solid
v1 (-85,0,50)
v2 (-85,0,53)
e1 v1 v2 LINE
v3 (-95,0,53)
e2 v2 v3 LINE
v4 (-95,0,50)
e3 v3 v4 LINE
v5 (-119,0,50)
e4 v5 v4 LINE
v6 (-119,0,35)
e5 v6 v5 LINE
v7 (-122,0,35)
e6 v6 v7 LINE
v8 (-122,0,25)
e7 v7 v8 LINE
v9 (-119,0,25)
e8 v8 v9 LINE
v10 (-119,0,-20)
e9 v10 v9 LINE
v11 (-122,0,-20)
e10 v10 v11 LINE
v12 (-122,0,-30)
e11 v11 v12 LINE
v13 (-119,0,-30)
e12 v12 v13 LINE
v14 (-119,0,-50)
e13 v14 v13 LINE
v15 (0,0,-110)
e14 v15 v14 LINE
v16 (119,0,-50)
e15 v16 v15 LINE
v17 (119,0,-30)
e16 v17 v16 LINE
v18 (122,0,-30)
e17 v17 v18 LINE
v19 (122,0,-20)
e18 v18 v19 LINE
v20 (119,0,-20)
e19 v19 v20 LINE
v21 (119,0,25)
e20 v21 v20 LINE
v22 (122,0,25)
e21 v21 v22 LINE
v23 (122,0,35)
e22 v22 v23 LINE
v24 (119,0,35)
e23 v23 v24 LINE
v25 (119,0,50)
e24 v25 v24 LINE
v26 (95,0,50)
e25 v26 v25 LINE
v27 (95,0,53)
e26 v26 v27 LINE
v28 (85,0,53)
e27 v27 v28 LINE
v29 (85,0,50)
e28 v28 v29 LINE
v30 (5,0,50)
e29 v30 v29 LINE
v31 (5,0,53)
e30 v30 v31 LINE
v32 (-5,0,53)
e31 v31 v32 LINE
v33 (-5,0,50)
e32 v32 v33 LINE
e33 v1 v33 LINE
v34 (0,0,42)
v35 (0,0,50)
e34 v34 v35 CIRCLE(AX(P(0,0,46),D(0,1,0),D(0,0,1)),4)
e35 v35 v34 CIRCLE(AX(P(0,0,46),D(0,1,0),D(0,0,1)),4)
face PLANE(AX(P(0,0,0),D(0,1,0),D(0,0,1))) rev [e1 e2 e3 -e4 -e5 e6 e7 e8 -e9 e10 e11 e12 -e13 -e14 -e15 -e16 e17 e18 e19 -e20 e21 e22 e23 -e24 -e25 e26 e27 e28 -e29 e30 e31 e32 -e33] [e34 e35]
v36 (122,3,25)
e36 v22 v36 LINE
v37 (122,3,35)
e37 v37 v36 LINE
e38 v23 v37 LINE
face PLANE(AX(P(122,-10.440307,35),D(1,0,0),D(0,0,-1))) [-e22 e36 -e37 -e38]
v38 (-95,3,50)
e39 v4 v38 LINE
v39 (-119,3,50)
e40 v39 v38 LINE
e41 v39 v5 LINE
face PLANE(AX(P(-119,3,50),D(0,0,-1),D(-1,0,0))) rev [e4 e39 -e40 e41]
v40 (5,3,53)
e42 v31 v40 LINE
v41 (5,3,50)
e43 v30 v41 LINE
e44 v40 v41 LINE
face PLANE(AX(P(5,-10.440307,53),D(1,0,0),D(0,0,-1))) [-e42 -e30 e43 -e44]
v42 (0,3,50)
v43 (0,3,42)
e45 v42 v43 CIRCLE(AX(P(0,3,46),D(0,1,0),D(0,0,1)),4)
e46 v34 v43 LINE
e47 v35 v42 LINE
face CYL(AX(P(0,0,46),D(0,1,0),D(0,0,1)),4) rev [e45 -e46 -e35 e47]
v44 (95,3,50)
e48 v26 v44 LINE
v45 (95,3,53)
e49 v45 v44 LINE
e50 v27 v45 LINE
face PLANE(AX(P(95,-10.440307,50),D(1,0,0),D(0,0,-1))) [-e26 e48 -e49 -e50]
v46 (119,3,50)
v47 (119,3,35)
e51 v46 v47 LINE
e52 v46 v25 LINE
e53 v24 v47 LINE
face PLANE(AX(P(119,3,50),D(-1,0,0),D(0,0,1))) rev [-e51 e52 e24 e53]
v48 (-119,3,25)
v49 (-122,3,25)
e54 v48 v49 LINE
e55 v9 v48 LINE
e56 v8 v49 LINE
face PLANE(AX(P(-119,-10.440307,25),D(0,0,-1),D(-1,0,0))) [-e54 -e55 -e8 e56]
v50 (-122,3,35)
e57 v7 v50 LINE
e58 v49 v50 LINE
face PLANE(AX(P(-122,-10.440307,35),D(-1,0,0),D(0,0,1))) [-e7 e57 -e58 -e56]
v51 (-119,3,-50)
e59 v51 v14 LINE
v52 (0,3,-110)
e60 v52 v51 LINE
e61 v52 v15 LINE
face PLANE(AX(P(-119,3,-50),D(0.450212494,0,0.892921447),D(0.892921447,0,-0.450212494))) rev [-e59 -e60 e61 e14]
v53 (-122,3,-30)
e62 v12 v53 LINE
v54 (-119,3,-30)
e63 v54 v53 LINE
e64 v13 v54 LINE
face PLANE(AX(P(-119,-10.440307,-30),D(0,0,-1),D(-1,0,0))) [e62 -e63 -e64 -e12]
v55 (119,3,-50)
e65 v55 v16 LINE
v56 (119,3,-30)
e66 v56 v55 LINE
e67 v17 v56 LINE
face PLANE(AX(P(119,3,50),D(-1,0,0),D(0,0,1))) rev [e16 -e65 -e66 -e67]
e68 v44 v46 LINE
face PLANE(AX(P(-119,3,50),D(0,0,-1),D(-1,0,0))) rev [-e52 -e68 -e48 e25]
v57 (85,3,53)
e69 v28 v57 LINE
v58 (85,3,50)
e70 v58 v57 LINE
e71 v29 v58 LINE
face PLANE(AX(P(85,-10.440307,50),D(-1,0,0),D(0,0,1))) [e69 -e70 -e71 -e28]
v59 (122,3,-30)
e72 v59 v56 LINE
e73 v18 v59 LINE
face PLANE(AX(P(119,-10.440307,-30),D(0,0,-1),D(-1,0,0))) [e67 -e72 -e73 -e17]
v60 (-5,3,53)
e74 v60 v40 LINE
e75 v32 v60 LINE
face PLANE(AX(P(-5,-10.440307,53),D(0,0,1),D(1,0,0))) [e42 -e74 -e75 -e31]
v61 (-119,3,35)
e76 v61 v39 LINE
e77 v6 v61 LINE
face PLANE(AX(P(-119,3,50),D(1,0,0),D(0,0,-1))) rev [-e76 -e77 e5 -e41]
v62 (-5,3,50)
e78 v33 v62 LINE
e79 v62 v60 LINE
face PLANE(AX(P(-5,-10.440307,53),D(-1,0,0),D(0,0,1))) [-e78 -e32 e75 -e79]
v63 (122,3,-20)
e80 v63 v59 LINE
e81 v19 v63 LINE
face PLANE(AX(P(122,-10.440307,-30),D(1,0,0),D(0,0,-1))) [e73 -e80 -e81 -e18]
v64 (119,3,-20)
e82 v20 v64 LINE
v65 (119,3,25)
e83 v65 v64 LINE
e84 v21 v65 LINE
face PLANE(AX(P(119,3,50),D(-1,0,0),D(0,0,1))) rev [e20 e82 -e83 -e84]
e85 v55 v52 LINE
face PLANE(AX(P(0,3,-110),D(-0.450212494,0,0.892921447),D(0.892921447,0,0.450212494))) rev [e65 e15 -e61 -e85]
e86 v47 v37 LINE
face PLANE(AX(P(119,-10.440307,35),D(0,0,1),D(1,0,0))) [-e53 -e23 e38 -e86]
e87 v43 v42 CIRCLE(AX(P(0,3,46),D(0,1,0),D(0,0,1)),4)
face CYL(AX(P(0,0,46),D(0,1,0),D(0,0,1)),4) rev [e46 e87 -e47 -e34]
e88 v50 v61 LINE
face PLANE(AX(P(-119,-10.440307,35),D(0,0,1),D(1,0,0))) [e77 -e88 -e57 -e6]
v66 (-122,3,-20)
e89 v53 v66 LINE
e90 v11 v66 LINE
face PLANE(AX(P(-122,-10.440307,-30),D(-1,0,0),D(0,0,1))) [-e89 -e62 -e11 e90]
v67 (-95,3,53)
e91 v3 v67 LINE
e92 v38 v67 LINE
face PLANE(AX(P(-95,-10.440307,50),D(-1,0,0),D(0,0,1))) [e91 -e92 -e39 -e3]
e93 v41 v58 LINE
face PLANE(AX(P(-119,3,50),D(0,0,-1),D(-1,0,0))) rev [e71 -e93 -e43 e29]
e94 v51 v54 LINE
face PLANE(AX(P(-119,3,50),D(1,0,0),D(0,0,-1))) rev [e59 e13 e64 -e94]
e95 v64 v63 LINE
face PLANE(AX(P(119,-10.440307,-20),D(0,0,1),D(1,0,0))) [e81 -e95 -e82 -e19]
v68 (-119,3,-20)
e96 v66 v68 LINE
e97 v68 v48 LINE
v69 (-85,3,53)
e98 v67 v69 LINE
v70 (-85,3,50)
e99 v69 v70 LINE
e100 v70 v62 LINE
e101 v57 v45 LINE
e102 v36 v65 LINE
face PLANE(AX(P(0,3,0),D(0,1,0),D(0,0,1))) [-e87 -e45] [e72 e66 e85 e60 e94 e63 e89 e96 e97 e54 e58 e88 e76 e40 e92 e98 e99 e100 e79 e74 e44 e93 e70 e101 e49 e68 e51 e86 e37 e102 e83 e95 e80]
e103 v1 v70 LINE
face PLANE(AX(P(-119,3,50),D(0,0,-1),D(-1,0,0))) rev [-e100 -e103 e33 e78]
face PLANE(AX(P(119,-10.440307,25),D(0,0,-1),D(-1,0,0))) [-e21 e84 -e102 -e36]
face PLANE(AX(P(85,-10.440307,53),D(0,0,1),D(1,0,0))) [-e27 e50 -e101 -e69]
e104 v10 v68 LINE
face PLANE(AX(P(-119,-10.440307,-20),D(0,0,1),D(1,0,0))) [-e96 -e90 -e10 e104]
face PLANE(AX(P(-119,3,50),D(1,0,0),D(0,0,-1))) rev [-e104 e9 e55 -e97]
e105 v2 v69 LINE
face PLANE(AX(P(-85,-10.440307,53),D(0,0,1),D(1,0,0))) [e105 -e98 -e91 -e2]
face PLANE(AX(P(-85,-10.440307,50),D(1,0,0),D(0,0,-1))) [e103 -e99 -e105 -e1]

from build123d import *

# Parameters (mm, degrees)
BOSS_EXTRUDE1_DEPTH = 3
SKETCH3_W           = 3
SKETCH3_H           = 10
SKETCH3_W_2         = 10
SKETCH3_H_2         = 3
BOSS_EXTRUDE2_DEPTH = 3
SKETCH4_R           = 4
CUT_EXTRUDE1_DEPTH  = 165.295465549


with BuildPart() as part:
    # Sketch1 → Boss-Extrude1 (new body)
    with BuildSketch(Plane(origin=(0, 0, 0), x_dir=(1, 0, 0), z_dir=(0, 1, 0))):
        Polygon((-119, 50), (0, 110), (119, 50), (119, -50), (-119, -50), align=None)
    extrude(amount=BOSS_EXTRUDE1_DEPTH)

    # Sketch3 → Boss-Extrude2 (add)
    with BuildSketch(Plane(origin=(0, 3, 0), x_dir=(1, 0, 0), z_dir=(0, 1, 0))):
        with Locations((120.5, 25)):
            Rectangle(SKETCH3_W, SKETCH3_H)
        with Locations((120.5, -30)):
            Rectangle(SKETCH3_W, SKETCH3_H)
        with Locations((-120.5, -30)):
            Rectangle(SKETCH3_W, SKETCH3_H)
        with Locations((-120.5, 25)):
            Rectangle(SKETCH3_W, SKETCH3_H)
        with Locations((-90, -51.5)):
            Rectangle(SKETCH3_W_2, SKETCH3_H_2)
        with Locations((90, -51.5)):
            Rectangle(SKETCH3_W_2, SKETCH3_H_2)
        with Locations((0, -51.5)):
            Rectangle(SKETCH3_W_2, SKETCH3_H_2)
    extrude(amount=-BOSS_EXTRUDE2_DEPTH)

    # Sketch4 → Cut-Extrude1 (cut, through all)
    with BuildSketch(Plane(origin=(0, 3, 0), x_dir=(1, 0, 0), z_dir=(0, 1, 0))):
        with Locations(Location((0, -46, 0), (0, 0, 270))):
            Circle(SKETCH4_R)
    extrude(amount=-CUT_EXTRUDE1_DEPTH, mode=Mode.SUBTRACT)


solid = part.part
